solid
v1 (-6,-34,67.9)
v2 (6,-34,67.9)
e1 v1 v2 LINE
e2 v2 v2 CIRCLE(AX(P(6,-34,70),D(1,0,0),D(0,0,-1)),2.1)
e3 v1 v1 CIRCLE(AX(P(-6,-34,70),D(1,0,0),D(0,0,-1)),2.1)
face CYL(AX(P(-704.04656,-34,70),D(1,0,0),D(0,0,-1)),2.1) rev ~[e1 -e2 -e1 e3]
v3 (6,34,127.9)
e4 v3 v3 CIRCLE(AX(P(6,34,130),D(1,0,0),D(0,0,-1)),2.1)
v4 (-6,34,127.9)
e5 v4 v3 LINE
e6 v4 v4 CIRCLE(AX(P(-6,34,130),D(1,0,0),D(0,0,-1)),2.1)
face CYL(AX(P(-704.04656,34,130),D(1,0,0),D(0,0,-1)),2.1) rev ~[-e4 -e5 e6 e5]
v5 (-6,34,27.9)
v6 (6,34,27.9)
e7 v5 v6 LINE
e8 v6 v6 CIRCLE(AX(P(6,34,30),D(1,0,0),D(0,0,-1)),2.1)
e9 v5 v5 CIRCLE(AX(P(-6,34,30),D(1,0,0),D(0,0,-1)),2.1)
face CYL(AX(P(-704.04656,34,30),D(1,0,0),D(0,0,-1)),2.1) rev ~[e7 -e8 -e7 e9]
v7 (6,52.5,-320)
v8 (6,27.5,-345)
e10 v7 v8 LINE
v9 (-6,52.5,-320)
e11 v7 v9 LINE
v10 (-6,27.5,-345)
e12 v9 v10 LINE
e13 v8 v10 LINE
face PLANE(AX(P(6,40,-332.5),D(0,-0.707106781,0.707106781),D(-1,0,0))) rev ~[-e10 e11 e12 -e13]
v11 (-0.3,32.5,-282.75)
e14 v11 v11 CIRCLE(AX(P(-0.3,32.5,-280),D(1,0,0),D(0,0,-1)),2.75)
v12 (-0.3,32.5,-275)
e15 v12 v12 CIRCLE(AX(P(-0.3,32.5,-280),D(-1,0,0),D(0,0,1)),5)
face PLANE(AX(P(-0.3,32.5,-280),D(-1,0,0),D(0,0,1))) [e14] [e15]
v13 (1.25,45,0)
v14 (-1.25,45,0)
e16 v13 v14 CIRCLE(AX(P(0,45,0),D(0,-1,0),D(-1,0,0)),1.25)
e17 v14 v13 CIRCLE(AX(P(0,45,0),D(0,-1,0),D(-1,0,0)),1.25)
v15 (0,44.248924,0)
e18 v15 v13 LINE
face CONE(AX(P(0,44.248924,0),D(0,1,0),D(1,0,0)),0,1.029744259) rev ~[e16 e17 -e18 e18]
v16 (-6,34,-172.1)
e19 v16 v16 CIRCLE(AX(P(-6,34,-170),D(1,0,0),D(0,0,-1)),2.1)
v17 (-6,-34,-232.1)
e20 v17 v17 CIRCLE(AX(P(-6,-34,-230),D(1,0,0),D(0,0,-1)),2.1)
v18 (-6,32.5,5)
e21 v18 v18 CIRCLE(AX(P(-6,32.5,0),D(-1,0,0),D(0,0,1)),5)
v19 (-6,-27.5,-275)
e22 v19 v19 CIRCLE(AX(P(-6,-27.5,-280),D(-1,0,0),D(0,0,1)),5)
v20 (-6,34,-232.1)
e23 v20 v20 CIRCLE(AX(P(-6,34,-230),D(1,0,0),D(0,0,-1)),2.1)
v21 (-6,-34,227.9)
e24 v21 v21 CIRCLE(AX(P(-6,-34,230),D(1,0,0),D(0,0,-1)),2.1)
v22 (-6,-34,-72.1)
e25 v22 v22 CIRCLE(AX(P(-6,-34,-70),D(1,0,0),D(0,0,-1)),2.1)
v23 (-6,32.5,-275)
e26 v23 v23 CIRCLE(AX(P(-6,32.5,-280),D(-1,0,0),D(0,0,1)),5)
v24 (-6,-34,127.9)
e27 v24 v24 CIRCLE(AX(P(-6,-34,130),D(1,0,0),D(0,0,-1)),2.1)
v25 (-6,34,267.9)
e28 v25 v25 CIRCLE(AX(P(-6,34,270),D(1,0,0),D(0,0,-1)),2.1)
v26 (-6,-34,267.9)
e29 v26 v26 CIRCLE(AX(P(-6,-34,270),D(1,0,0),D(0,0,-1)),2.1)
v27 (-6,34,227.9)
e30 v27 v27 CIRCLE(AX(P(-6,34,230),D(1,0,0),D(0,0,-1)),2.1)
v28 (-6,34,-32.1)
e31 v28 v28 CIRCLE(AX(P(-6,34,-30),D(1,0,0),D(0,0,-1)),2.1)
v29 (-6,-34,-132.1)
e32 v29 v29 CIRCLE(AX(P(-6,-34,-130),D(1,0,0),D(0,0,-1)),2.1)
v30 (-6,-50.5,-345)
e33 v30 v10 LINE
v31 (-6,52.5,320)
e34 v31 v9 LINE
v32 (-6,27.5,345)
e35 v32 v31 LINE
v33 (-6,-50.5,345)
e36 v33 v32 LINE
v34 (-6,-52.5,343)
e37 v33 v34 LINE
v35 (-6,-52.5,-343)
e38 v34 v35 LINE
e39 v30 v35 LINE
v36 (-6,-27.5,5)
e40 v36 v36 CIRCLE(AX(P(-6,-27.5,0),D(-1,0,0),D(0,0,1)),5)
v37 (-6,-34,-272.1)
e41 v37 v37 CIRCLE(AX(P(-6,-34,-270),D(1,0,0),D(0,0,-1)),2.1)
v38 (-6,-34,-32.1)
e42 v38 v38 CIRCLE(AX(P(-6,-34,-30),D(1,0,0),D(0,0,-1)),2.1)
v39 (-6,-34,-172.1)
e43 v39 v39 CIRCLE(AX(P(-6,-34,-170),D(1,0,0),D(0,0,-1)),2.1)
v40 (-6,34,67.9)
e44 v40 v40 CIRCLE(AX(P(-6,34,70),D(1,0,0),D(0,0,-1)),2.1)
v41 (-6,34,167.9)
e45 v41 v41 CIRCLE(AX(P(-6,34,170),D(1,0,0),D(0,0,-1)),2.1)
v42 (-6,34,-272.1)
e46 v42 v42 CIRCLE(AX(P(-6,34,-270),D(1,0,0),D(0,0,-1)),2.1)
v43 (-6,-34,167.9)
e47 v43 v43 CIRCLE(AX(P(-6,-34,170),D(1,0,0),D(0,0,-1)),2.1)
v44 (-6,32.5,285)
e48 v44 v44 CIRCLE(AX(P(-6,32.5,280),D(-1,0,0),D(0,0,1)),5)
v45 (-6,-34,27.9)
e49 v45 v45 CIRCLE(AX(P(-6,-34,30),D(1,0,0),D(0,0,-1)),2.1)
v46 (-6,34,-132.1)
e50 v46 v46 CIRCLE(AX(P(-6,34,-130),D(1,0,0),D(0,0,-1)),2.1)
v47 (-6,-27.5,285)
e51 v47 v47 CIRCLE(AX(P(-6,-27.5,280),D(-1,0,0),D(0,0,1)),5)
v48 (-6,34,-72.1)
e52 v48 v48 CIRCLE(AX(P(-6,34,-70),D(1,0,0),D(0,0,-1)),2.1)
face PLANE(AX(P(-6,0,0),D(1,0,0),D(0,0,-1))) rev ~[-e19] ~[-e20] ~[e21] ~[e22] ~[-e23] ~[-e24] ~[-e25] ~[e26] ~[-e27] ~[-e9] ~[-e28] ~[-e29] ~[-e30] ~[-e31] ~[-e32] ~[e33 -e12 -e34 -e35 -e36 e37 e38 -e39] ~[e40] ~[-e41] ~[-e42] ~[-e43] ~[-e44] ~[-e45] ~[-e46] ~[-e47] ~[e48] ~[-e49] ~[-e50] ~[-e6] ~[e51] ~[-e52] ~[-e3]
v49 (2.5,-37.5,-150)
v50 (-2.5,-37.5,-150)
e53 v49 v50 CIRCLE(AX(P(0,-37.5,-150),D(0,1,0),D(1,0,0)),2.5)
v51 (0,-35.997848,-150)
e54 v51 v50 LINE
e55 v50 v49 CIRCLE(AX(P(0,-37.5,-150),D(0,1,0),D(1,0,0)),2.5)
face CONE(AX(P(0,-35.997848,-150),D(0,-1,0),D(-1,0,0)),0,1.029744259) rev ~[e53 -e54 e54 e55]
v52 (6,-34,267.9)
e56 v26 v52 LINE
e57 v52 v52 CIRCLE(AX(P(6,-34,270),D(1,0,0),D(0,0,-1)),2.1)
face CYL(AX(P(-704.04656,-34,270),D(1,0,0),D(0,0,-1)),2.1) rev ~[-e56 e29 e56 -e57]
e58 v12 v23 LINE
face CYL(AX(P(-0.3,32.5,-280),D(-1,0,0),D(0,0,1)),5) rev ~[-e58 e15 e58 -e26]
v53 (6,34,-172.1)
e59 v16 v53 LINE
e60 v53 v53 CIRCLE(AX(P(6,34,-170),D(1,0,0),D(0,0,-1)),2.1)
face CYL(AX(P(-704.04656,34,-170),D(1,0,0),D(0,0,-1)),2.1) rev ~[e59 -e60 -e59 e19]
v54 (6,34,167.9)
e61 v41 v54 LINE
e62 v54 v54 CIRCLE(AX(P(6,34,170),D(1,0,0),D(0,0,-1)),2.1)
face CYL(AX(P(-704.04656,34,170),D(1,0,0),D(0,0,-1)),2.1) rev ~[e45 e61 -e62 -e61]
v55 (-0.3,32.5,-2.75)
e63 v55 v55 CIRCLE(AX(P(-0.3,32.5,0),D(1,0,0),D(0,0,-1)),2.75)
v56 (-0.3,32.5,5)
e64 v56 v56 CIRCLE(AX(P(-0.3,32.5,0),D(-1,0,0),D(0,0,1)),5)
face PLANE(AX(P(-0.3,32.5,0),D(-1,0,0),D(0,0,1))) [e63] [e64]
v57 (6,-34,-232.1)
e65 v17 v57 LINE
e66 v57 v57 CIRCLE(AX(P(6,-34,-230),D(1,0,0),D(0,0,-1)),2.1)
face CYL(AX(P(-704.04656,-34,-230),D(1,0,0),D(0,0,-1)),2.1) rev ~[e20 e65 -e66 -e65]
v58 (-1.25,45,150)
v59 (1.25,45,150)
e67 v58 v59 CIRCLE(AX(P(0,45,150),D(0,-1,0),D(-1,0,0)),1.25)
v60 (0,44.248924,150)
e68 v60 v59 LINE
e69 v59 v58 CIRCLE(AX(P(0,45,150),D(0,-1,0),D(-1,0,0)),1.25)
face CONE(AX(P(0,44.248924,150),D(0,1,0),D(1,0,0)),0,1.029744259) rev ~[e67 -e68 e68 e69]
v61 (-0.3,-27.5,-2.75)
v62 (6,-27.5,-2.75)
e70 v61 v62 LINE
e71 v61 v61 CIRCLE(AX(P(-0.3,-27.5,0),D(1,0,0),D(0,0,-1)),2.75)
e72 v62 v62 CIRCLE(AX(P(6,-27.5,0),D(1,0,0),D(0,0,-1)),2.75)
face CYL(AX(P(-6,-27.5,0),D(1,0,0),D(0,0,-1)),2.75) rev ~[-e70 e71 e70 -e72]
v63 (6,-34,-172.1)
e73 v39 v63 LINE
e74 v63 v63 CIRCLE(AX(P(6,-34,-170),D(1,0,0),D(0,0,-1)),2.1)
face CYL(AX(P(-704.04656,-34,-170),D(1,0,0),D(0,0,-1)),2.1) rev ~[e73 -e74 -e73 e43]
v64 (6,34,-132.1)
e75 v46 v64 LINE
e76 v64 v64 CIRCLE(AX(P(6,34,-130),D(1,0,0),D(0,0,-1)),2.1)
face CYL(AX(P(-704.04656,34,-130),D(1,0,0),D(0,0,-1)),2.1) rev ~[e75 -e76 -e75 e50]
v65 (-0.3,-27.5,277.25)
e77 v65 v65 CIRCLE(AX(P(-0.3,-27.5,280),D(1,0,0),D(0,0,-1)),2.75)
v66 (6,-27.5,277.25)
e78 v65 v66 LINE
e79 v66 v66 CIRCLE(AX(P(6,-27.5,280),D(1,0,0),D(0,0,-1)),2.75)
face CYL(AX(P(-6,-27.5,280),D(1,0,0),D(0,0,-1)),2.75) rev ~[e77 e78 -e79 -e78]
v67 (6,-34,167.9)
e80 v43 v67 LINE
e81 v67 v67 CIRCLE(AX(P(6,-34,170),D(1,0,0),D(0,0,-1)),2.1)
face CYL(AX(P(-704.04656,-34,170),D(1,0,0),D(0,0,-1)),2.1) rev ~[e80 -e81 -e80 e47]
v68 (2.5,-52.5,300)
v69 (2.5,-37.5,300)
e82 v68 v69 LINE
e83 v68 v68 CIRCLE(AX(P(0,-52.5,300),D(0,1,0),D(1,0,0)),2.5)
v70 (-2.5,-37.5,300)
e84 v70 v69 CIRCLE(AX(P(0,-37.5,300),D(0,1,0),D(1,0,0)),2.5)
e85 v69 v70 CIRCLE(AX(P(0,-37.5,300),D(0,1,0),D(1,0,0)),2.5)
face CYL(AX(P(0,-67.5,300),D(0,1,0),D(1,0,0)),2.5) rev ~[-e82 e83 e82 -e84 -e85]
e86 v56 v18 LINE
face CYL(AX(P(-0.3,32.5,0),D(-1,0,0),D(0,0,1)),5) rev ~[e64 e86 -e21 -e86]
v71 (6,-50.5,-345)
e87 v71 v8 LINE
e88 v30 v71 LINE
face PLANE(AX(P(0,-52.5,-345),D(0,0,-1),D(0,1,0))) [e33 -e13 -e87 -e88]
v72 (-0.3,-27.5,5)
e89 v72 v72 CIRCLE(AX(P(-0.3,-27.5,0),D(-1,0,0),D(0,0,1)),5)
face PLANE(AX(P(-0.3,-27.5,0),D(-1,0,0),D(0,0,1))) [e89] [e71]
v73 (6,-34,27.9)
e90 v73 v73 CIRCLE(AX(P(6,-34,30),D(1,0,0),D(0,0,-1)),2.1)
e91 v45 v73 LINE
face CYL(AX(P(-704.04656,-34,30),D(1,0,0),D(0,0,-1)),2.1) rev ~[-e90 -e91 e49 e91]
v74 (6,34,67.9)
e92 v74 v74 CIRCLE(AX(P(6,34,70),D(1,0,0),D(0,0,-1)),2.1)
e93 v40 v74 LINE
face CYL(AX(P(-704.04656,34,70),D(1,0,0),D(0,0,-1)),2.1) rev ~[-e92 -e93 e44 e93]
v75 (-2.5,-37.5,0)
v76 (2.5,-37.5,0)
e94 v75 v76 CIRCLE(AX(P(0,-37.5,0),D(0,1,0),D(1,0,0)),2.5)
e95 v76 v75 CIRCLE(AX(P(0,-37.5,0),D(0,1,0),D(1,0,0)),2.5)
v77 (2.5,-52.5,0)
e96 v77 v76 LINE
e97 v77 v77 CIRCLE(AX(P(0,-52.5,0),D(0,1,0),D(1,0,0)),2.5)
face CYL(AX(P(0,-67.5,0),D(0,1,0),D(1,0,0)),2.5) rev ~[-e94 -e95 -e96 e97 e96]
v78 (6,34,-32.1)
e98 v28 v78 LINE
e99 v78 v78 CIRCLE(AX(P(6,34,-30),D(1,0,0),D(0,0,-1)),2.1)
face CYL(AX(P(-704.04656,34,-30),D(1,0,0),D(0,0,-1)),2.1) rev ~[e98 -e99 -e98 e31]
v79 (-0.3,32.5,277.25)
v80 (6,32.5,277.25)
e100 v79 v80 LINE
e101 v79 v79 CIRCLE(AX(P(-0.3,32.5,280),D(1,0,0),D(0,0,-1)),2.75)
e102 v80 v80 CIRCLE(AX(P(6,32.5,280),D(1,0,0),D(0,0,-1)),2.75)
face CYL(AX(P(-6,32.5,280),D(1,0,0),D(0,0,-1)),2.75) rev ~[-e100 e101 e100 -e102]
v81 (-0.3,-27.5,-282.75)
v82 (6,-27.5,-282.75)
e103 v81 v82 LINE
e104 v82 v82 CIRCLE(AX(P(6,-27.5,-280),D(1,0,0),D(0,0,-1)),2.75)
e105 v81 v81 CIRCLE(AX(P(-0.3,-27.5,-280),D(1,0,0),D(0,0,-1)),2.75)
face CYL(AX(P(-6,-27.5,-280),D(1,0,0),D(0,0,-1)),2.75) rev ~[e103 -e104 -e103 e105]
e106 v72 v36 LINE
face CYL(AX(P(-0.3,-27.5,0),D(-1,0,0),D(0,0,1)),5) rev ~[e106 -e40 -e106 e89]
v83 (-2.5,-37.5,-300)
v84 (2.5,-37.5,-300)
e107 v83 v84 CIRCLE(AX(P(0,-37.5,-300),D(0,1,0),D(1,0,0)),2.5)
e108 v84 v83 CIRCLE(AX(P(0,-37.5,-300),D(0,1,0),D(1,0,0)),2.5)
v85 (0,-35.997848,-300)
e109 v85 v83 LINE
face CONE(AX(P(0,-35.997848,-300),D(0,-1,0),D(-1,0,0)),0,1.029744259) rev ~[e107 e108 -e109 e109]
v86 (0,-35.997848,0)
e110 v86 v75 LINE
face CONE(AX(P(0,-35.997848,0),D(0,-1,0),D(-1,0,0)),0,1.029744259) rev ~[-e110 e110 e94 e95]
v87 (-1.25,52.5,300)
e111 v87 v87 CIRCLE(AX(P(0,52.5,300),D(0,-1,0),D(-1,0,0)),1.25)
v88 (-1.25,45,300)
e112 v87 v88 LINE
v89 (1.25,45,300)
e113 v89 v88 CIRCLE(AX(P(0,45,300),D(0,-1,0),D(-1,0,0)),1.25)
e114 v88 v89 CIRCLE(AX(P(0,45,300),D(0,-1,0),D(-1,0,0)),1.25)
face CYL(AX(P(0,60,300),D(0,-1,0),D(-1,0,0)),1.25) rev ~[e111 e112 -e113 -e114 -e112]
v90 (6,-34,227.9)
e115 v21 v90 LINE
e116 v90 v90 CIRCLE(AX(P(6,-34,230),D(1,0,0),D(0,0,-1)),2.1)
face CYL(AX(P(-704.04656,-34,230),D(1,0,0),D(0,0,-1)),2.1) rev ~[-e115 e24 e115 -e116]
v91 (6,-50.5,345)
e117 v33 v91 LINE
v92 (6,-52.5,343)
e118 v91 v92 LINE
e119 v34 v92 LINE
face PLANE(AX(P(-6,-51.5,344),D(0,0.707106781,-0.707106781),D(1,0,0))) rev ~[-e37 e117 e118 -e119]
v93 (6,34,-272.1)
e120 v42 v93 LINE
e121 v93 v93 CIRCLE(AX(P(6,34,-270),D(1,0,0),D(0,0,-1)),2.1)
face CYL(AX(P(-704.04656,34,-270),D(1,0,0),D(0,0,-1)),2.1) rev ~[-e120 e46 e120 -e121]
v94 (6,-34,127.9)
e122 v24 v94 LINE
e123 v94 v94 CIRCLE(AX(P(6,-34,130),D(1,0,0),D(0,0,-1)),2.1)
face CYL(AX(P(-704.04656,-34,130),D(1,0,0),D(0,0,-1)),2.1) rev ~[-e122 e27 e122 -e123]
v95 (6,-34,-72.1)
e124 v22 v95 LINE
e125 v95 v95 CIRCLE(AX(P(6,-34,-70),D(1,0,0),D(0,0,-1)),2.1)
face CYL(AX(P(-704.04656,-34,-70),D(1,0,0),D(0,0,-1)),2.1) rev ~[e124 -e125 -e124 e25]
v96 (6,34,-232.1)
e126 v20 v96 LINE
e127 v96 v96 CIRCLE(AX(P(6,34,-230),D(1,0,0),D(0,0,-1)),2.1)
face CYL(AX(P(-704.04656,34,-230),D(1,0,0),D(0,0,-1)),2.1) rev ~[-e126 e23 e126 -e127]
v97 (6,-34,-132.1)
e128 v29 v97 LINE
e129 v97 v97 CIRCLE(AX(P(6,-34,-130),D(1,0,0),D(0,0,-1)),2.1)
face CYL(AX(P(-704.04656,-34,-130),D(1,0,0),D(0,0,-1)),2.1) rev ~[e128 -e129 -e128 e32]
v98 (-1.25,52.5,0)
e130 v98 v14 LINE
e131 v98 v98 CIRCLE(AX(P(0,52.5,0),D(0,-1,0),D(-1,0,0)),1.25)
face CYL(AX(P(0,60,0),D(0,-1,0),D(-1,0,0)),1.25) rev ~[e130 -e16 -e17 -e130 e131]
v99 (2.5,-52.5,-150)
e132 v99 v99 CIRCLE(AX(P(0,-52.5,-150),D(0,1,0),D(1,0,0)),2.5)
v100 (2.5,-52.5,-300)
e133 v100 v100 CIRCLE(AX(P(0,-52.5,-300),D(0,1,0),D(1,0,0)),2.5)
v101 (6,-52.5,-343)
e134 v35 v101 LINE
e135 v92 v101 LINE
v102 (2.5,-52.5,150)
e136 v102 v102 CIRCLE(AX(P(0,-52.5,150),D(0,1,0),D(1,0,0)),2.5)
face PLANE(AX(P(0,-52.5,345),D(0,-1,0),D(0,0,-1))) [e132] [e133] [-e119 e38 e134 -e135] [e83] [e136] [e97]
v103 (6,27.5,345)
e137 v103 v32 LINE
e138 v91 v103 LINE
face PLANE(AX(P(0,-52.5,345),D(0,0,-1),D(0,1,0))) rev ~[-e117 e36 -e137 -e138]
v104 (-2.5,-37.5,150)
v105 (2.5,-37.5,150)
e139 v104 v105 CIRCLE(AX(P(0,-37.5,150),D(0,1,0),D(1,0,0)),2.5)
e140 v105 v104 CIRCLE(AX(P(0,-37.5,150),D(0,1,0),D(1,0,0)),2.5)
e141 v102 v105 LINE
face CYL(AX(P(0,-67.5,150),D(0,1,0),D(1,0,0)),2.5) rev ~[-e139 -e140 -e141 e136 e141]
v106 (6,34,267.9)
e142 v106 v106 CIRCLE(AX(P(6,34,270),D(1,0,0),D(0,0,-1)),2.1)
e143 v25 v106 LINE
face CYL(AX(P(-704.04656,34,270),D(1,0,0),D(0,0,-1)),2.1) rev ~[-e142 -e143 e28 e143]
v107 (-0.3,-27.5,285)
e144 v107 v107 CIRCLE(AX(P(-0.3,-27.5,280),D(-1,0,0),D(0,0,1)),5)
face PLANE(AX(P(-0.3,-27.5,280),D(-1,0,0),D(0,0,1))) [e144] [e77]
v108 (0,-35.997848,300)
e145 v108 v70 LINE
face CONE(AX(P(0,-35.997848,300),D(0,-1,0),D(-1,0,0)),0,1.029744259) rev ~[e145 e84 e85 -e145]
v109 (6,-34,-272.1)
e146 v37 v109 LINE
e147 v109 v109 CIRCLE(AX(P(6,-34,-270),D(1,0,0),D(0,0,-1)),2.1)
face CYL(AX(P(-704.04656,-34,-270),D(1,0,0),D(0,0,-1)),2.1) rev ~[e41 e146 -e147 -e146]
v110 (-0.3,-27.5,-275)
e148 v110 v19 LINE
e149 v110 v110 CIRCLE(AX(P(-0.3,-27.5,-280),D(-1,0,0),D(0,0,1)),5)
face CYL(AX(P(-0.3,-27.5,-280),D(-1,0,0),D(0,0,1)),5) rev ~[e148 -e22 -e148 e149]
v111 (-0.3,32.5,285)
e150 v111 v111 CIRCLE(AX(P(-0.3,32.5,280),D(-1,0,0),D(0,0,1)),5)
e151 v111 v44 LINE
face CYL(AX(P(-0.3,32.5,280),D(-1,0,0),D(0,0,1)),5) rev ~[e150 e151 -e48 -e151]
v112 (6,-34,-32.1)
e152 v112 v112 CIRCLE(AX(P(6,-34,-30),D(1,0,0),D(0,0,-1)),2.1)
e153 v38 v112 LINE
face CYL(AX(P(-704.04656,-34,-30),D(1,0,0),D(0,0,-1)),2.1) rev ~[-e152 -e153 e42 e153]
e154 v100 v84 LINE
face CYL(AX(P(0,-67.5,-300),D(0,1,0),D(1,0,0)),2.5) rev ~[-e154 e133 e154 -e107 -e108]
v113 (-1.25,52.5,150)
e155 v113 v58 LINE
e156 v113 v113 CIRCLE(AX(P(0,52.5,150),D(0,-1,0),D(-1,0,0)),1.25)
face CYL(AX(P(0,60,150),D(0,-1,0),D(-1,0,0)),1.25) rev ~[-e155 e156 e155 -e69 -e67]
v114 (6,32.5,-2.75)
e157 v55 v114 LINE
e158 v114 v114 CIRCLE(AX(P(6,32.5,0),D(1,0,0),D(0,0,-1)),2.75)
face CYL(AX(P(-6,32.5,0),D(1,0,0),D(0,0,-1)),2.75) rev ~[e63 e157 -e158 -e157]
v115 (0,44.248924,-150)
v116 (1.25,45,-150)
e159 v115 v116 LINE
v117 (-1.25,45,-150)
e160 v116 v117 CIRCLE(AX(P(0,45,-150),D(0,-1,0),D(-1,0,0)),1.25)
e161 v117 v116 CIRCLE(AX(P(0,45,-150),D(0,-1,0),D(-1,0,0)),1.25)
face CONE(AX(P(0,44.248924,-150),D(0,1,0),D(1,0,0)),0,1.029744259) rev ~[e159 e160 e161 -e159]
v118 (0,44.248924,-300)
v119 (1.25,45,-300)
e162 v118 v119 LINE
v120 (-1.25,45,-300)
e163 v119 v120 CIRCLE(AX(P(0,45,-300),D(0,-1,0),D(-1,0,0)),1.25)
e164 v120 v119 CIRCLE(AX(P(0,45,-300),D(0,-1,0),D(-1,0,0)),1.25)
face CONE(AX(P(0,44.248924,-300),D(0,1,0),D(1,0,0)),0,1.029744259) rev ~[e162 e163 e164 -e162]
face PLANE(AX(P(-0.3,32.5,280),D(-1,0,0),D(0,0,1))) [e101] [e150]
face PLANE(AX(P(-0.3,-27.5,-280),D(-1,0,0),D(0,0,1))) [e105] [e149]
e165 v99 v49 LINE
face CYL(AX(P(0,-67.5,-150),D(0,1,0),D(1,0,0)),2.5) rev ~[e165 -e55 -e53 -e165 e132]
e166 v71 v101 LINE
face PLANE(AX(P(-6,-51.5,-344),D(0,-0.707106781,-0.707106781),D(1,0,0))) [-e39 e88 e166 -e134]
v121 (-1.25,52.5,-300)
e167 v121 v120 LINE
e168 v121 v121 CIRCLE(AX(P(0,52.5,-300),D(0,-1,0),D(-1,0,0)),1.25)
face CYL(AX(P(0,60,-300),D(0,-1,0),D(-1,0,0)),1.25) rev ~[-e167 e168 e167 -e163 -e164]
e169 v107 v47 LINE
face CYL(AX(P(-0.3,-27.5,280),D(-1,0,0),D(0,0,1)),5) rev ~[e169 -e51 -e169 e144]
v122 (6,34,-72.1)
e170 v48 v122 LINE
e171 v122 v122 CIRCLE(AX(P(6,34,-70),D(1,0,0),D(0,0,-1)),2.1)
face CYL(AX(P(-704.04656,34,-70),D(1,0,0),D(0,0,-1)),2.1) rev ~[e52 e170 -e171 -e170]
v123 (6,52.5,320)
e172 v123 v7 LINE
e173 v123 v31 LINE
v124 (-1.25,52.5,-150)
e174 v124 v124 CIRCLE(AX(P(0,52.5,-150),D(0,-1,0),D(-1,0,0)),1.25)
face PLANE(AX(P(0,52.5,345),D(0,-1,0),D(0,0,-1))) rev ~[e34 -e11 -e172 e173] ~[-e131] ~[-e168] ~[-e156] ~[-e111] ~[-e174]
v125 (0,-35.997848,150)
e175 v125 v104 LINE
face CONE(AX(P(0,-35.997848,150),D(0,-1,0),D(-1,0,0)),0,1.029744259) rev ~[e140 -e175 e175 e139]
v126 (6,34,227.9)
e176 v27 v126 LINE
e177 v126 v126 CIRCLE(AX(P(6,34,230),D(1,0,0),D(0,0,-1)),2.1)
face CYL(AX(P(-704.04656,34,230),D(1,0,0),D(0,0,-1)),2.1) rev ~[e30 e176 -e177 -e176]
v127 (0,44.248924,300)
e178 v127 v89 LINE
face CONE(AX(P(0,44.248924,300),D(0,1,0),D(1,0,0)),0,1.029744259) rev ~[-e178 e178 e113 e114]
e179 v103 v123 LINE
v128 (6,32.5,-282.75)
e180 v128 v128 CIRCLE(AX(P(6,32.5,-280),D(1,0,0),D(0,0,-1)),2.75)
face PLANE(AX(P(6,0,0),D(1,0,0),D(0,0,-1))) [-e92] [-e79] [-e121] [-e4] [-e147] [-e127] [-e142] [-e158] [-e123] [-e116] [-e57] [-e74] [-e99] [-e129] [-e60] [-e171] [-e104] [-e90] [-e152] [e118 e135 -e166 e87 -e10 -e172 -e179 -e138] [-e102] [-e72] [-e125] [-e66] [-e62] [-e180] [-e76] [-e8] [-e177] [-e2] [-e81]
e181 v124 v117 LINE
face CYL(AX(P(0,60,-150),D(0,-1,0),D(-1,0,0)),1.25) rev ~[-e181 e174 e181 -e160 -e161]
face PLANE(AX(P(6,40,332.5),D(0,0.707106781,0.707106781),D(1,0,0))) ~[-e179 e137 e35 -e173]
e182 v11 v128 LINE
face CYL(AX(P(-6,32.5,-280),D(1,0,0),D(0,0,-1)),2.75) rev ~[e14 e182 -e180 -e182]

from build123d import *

# Parameters (mm, degrees)
SKETCH_1_W                = 690
SKETCH_1_H                = 105
EXTRUDE_1_DEPTH           = 6
CHAMFER_1_SIZE            = 2
CHAMFER_2_SIZE            = 25
HOLE_WIZARD_M6_1_D        = 5
HOLE_WIZARD_M6_1_DEPTH    = 15
HOLE_WIZARD_M6_1_TIP      = 1.502151548
HOLE_WIZARD_1_D           = 5.5
HOLE_WIZARD_1_CBORE_D     = 10
HOLE_WIZARD_1_CBORE_DEPTH = 5.7
HOLE_WIZARD_M5_1_D        = 4.2
HOLE_WIZARD_M3_2_D        = 2.5
HOLE_WIZARD_M3_2_DEPTH    = 7.5
HOLE_WIZARD_M3_2_TIP      = 0.751075774


with BuildPart() as part:
    # 草图1 → 凸台-拉伸1 (new, symmetric)
    with BuildSketch(Plane(origin=(0, 0, 0), x_dir=(0, 0, -1), z_dir=(1, 0, 0))):
        Rectangle(SKETCH_1_W, SKETCH_1_H)
    extrude(amount=EXTRUDE_1_DEPTH, both=True)

    # 倒角1
    chamfer_1_edges = [part.edges().sort_by_distance(p)[0] for p in [
        (0, -52.5, -345),
        (0, -52.5, 345),
    ]]
    chamfer(chamfer_1_edges, length=CHAMFER_1_SIZE)

    # 倒角2
    chamfer_2_edges = [part.edges().sort_by_distance(p)[0] for p in [
        (0, 52.5, 345),
        (0, 52.5, -345),
    ]]
    chamfer(chamfer_2_edges, length=CHAMFER_2_SIZE)

    # M6 螺纹孔1
    with Locations(Plane(origin=(0, -52.5, 0), x_dir=(-1, 0, 0), z_dir=(0, -1, 0))):
        with Locations((0, -300), (0, -150), (0, 0), (0, 150), (0, 300)):
            Hole(HOLE_WIZARD_M6_1_D / 2, depth=HOLE_WIZARD_M6_1_DEPTH)
            with Locations((0, 0, -(HOLE_WIZARD_M6_1_DEPTH + HOLE_WIZARD_M6_1_TIP / 2))):  # 118° drill point
                Cone(0, HOLE_WIZARD_M6_1_D / 2, HOLE_WIZARD_M6_1_TIP, mode=Mode.SUBTRACT)

    # 打孔尺寸(%根据)内六角圆柱头螺钉的类型1 (through all)
    with Locations(Plane.ZY.offset(6)):
        with Locations((280, 32.5), (280, -27.5), (0, 32.5), (0, -27.5), (-280, 32.5), (-280, -27.5)):
            CounterBoreHole(HOLE_WIZARD_1_D / 2, HOLE_WIZARD_1_CBORE_D / 2, HOLE_WIZARD_1_CBORE_DEPTH)

    # M5 螺纹孔1 (through all)
    with Locations(Plane.ZY.offset(6)):
        with Locations((270, 34), (270, -34), (170, 34), (170, -34), (70, 34), (70, -34), (-30, 34), (-30, -34), (-130, 34), (-130, -34), (130, -34), (130, 34), (30, -34), (30, 34), (-70, -34), (-70, 34), (-170, -34), (-170, 34), (-270, -34), (-270, 34), (-230, 34), (-230, -34), (230, -34), (230, 34)):
            Hole(HOLE_WIZARD_M5_1_D / 2)

    # M3 螺纹孔2
    with Locations(Plane(origin=(0, 52.5, 0), x_dir=(1, 0, 0), z_dir=(0, 1, 0))):
        with Locations((0, -300), (0, -150), (0, 0), (0, 150), (0, 300)):
            Hole(HOLE_WIZARD_M3_2_D / 2, depth=HOLE_WIZARD_M3_2_DEPTH)
            with Locations((0, 0, -(HOLE_WIZARD_M3_2_DEPTH + HOLE_WIZARD_M3_2_TIP / 2))):  # 118° drill point
                Cone(0, HOLE_WIZARD_M3_2_D / 2, HOLE_WIZARD_M3_2_TIP, mode=Mode.SUBTRACT)


solid = part.part
